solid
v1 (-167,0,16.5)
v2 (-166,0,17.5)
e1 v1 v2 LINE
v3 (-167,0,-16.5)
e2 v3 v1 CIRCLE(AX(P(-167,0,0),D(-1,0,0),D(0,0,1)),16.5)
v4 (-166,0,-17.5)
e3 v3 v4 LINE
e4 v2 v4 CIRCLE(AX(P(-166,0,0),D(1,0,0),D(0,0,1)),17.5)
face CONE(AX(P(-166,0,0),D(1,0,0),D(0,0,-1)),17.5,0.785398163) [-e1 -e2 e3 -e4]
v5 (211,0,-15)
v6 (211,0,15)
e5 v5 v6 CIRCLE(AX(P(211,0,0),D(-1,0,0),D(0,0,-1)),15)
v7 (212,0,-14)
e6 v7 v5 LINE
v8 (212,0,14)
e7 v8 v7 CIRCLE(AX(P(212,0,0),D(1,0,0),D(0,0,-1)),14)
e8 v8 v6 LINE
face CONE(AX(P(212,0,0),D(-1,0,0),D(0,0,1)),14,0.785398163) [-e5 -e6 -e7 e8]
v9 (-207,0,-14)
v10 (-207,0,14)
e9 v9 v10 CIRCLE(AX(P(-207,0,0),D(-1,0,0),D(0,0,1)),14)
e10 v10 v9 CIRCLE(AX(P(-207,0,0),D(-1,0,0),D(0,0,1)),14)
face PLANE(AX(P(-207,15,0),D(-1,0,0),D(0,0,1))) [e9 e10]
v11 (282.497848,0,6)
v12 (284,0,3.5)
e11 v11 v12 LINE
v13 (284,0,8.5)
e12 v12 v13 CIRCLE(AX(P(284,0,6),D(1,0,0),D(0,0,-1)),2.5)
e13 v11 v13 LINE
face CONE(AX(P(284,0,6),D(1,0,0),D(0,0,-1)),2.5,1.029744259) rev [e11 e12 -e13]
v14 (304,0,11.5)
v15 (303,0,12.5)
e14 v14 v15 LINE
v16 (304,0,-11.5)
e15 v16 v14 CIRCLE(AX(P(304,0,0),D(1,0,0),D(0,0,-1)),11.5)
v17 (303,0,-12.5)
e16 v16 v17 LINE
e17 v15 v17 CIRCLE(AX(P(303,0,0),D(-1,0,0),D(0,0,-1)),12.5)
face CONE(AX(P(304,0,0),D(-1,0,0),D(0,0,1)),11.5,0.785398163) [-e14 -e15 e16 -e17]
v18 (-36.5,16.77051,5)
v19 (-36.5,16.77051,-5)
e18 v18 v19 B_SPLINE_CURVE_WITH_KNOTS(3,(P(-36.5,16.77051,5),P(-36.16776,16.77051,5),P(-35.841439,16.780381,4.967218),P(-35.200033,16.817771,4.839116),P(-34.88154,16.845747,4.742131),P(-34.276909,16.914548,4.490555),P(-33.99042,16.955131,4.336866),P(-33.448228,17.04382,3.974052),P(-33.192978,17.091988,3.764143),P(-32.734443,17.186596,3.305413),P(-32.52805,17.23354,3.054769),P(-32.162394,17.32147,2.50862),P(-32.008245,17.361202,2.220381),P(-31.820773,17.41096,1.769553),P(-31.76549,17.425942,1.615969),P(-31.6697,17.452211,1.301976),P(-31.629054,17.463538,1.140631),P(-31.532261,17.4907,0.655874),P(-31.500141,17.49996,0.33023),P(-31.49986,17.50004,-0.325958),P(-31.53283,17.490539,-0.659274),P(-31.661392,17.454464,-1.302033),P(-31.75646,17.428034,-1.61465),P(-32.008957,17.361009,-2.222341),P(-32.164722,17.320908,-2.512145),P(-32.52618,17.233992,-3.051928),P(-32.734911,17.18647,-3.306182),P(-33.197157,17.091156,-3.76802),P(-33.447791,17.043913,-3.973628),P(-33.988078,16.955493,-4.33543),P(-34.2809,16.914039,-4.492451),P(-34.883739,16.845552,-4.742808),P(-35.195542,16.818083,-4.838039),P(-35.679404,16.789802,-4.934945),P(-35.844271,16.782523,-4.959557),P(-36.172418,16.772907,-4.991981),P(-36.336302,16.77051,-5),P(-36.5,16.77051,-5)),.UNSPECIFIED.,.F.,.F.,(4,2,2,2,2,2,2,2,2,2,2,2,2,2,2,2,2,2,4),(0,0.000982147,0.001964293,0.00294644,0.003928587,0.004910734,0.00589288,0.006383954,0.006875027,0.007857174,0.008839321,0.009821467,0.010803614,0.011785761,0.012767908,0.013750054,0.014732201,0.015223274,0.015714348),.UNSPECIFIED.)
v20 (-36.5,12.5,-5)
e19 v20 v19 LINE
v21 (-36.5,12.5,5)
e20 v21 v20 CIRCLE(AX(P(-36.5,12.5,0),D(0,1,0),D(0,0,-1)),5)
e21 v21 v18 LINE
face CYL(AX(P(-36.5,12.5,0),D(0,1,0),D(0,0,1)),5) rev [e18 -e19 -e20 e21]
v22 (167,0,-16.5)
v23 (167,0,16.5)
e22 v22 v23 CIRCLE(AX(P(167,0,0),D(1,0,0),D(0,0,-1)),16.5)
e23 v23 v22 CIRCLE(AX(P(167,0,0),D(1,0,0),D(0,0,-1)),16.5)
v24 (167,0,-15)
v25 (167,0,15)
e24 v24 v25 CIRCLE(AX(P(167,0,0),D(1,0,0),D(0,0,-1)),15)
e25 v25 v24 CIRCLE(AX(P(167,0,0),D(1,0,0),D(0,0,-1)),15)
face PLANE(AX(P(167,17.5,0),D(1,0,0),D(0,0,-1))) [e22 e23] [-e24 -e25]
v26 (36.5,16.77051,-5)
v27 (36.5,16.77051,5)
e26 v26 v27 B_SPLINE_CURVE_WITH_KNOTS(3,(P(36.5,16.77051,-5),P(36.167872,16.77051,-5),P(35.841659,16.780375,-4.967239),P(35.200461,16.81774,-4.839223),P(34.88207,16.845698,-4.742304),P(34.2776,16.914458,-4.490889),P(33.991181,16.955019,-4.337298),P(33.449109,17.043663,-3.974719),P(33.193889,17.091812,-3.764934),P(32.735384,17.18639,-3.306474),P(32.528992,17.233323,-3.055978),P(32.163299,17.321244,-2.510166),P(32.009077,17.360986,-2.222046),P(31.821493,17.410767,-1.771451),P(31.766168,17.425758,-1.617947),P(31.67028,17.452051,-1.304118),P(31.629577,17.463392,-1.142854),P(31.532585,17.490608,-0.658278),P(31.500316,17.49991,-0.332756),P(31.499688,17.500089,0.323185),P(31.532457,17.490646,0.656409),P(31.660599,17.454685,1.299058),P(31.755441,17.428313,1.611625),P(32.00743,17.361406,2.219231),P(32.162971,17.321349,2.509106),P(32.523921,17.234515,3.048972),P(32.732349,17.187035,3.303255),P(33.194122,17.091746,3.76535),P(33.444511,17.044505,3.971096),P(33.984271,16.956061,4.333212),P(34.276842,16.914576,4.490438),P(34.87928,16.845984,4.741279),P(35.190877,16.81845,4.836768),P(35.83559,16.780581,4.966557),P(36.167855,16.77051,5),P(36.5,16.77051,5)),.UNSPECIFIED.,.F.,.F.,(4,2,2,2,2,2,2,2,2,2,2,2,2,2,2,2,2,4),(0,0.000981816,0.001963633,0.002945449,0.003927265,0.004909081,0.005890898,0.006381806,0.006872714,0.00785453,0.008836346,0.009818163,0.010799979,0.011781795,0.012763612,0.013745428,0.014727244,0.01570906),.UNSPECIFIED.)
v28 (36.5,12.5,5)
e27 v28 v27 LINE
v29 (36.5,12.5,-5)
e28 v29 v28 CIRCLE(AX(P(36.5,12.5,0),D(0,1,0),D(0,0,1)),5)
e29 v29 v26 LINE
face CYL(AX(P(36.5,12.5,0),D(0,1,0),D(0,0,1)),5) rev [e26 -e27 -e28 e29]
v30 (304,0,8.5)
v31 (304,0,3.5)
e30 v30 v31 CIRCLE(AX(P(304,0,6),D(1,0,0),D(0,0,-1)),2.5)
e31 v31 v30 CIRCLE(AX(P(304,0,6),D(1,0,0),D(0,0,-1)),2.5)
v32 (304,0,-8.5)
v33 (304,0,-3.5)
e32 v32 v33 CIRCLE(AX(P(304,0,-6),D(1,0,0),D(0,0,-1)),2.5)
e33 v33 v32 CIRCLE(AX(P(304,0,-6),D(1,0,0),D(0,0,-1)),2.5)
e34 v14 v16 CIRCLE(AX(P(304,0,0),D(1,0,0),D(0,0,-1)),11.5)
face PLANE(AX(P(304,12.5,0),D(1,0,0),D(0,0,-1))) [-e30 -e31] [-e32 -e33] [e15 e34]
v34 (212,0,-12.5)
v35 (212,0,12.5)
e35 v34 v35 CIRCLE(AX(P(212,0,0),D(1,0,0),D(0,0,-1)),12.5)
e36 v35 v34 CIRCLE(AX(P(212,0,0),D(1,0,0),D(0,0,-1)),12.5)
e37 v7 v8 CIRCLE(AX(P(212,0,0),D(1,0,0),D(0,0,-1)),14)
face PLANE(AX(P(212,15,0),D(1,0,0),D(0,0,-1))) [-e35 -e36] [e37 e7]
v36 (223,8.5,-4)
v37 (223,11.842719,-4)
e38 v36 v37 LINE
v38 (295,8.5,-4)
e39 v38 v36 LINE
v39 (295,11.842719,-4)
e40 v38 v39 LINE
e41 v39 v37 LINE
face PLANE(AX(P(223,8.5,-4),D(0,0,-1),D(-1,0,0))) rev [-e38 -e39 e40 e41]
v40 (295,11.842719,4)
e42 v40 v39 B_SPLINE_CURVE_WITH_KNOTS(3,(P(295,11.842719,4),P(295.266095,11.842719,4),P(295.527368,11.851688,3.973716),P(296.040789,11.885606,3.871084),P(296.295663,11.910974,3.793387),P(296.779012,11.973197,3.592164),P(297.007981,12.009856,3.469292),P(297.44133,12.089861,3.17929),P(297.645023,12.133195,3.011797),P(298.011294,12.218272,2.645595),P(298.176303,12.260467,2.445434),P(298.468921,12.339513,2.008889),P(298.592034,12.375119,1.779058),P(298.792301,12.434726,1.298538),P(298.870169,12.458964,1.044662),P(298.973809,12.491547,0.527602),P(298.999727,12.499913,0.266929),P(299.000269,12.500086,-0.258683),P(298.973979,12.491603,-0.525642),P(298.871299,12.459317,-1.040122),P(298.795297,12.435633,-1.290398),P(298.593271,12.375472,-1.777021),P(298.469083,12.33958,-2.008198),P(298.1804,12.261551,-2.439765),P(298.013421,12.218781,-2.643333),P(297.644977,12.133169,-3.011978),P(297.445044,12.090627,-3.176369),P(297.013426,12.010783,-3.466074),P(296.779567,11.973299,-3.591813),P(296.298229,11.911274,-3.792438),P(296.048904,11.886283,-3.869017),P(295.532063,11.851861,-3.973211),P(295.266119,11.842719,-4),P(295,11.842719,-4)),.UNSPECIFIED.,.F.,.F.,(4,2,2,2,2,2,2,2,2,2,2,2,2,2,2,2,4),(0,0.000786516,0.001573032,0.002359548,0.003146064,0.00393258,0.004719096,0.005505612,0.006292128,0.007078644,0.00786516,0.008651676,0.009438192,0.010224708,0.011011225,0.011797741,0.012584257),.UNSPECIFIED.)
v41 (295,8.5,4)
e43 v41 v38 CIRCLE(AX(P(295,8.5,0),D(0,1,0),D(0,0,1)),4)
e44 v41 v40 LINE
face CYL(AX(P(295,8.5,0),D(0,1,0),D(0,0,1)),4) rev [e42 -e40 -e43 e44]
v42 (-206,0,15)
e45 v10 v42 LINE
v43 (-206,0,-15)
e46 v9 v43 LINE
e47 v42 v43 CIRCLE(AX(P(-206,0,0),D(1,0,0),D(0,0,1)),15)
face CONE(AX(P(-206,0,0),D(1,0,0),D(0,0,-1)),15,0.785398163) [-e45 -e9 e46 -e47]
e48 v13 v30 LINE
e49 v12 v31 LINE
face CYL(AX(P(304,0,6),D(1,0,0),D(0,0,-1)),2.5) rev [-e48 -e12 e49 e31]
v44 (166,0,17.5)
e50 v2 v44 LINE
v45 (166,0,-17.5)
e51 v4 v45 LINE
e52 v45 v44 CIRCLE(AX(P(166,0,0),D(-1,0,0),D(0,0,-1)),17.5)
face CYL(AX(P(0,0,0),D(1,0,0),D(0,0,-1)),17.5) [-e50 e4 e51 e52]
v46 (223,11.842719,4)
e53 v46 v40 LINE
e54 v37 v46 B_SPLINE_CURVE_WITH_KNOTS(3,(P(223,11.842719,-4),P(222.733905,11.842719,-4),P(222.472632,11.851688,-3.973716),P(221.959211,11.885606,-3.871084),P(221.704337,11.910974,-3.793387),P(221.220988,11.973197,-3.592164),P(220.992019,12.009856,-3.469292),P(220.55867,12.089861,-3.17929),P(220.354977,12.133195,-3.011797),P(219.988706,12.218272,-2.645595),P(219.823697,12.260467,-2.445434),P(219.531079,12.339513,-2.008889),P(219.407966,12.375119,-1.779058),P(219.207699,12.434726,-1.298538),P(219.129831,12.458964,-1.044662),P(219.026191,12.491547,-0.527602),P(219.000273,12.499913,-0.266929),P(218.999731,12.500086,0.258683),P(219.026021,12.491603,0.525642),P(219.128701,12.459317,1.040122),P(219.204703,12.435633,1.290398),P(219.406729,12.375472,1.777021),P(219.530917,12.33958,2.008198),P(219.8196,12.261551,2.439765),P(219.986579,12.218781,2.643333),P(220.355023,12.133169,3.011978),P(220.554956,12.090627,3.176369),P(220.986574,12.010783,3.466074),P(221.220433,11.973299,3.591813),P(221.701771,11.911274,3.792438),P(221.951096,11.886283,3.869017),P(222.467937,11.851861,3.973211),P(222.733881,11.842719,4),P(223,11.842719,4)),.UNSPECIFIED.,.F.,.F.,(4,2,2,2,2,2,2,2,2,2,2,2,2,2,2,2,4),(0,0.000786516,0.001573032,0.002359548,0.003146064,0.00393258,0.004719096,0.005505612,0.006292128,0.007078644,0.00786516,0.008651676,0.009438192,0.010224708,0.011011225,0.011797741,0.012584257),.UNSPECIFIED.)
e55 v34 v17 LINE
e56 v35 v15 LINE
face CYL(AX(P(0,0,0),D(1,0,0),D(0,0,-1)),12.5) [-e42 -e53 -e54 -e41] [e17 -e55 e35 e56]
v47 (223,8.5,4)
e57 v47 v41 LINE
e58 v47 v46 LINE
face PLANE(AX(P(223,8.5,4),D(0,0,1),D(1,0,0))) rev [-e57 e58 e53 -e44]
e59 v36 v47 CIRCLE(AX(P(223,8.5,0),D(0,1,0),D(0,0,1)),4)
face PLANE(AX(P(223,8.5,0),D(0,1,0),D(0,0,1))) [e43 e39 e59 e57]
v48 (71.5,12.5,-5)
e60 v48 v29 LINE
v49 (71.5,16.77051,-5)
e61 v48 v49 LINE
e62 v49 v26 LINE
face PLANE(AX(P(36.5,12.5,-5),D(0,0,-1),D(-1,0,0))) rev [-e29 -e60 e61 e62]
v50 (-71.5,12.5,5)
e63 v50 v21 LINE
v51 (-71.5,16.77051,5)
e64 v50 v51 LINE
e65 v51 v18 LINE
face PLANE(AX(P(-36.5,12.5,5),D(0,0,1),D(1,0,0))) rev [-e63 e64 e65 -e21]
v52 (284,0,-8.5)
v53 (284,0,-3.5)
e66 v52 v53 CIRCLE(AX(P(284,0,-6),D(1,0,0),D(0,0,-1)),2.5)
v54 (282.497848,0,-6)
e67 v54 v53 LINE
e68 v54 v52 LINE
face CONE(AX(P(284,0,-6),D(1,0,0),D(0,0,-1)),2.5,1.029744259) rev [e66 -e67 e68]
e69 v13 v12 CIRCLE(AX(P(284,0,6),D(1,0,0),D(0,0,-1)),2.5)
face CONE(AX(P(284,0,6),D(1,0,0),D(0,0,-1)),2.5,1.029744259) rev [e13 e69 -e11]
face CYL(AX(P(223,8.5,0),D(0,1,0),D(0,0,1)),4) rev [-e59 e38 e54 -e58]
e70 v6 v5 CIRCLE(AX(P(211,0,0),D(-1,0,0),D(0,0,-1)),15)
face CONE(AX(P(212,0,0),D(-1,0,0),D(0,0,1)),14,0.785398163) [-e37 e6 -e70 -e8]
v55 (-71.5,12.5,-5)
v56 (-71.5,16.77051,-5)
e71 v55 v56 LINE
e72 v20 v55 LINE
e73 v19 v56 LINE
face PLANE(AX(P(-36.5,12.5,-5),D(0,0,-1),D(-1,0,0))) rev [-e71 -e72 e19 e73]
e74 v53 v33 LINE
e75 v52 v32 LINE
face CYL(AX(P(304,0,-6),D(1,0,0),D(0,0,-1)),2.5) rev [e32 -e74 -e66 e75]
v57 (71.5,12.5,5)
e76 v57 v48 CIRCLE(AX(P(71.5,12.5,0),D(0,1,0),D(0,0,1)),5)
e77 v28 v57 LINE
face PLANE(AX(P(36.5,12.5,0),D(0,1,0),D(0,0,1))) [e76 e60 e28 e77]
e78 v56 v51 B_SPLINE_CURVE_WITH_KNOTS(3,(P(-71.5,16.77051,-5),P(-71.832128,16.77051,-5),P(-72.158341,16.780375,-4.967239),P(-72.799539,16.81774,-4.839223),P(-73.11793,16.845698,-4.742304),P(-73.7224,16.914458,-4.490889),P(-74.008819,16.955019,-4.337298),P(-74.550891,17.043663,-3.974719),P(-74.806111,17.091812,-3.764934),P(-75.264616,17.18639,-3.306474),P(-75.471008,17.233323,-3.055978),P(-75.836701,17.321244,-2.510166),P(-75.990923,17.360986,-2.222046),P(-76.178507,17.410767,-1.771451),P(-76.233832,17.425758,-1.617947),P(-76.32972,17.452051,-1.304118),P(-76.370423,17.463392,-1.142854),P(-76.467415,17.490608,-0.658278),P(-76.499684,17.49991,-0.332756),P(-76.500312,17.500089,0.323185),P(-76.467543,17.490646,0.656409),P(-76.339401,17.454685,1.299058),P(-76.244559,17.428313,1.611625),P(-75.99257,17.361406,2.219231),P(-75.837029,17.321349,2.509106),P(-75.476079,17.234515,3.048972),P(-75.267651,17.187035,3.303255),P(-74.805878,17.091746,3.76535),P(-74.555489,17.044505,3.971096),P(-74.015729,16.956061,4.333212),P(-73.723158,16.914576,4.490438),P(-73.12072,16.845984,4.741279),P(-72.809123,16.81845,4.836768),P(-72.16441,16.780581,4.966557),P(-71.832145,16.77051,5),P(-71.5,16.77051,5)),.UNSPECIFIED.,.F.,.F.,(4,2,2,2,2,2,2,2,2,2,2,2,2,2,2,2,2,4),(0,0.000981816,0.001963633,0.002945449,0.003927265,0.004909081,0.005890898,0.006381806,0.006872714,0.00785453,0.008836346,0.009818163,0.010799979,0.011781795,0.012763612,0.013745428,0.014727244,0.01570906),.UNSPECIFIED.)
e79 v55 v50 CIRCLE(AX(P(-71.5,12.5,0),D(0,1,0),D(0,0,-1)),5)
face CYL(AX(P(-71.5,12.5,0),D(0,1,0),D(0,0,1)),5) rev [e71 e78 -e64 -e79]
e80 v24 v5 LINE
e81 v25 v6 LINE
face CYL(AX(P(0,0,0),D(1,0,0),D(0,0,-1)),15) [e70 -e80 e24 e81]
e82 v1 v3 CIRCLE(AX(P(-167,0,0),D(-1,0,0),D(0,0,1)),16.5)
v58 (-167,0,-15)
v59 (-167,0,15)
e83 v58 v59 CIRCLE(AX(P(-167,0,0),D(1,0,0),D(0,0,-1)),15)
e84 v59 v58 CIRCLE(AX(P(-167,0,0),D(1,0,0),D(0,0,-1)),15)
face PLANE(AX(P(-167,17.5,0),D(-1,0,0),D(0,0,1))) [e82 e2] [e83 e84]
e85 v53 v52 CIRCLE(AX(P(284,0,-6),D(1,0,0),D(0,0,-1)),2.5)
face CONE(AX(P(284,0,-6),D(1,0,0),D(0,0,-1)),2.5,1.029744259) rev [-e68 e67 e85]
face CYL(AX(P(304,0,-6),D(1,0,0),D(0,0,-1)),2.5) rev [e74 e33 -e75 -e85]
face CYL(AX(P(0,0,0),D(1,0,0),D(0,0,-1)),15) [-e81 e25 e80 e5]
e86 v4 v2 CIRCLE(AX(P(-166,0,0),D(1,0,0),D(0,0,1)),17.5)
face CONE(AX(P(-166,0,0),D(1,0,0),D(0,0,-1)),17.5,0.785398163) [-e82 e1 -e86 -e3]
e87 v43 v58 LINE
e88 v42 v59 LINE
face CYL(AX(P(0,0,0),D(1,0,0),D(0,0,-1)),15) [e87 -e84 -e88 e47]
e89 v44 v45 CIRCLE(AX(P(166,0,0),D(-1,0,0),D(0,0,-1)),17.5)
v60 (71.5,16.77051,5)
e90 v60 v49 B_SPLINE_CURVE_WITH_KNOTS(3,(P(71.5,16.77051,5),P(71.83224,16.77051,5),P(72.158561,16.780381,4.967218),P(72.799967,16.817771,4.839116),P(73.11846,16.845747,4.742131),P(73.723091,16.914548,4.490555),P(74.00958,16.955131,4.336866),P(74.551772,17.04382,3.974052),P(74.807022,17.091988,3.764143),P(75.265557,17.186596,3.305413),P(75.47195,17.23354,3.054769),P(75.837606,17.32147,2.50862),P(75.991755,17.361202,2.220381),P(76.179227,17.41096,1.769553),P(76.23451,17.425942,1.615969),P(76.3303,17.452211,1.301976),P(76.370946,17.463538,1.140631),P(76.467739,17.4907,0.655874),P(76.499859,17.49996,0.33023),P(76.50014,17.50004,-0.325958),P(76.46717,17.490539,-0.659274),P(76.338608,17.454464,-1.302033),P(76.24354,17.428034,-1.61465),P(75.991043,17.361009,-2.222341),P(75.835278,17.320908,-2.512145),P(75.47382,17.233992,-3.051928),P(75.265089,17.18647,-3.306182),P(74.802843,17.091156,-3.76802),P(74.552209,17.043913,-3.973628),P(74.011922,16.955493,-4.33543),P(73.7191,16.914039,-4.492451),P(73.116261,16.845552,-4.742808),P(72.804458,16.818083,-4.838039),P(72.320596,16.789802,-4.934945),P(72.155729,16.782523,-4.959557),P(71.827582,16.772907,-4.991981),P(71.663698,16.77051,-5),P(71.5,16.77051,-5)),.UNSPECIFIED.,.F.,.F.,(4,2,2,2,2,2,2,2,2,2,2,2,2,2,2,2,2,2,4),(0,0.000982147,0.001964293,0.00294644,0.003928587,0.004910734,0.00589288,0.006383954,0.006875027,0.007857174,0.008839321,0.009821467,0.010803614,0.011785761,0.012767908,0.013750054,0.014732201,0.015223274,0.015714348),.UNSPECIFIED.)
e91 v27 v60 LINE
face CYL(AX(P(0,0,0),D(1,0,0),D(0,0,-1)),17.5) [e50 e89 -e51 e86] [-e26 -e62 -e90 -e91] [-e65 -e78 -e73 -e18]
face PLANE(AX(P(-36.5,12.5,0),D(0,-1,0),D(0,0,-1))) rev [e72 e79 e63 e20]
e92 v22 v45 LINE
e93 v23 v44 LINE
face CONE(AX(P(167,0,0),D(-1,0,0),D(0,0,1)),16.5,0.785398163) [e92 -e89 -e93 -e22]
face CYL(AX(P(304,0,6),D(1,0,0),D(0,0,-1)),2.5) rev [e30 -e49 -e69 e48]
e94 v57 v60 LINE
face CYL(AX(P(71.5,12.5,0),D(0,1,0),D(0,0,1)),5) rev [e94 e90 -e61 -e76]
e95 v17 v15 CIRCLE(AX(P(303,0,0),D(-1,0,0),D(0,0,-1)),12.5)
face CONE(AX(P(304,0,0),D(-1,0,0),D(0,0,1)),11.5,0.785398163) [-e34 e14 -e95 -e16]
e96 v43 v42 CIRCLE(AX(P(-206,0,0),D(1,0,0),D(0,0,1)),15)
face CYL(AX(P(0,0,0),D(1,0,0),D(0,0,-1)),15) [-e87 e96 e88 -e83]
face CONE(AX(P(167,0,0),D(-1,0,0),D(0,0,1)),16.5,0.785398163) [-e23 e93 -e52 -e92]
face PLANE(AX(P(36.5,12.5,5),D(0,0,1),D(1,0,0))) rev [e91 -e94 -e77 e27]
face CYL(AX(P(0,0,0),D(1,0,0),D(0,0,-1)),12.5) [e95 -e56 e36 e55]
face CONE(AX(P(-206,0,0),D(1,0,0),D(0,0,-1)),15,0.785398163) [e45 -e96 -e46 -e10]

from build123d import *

# Parameters (mm, degrees)
CUT_EXTRUDE_1_DEPTH    = 5
CUT_EXTRUDE_2_DEPTH    = 4
CHAMFER_1_SIZE         = 1
HOLE_WIZARD_M6_1_D     = 5
HOLE_WIZARD_M6_1_DEPTH = 20
HOLE_WIZARD_M6_1_TIP   = 1.502151548


with BuildPart() as part:
    # 草图1 → 旋转1 (revolve)
    with BuildSketch(Plane.XY, mode=Mode.PRIVATE) as revolve_1_sk:
        Polygon((167, 17.5), (0, 17.5), (-167, 17.5), (-167, 15), (-207, 15), (-207, 0), (304, 0), (304, 12.5), (212, 12.5), (212, 15), (167, 15), align=None)
    revolve(revolve_1_sk.sketch.rotate(Axis((0, 0, 0), (-1, 0, 0)), 90), axis=Axis((0, 0, 0), (-1, 0, 0)))

    # 草图2 → 切除-拉伸1 (cut)
    with BuildSketch(Plane(origin=(0, 17.5, 0), x_dir=(1, 0, 0), z_dir=(0, 1, 0))):
        with BuildLine():
            Line((36.5, 5), (71.5, 5))
            ThreePointArc((71.5, 5), (76.5, 0), (71.5, -5))
            Line((71.5, -5), (36.5, -5))
            ThreePointArc((36.5, -5), (31.5, 0), (36.5, 5))
        make_face()
        with BuildLine():
            Line((-36.5, 5), (-71.5, 5))
            ThreePointArc((-71.5, 5), (-76.5, 0), (-71.5, -5))
            Line((-71.5, -5), (-36.5, -5))
            ThreePointArc((-36.5, -5), (-31.5, 0), (-36.5, 5))
        make_face()
    extrude(amount=-CUT_EXTRUDE_1_DEPTH, mode=Mode.SUBTRACT)

    # 草图3 → 切除-拉伸2 (cut)
    with BuildSketch(Plane(origin=(0, 12.5, 0), x_dir=(1, 0, 0), z_dir=(0, 1, 0))):
        with BuildLine():
            Line((223, 4), (295, 4))
            ThreePointArc((295, 4), (299, 0), (295, -4))
            Line((295, -4), (223, -4))
            ThreePointArc((223, -4), (219, 0), (223, 4))
        make_face()
    extrude(amount=-CUT_EXTRUDE_2_DEPTH, mode=Mode.SUBTRACT)

    # 倒角1
    chamfer_1_edges = [part.edges().sort_by_distance(p)[0] for p in [
        (-207, 0, 15),
        (-167, 0, 17.5),
        (167, 0, 17.5),
        (212, 0, 15),
        (304, 0, 12.5),
    ]]
    chamfer(chamfer_1_edges, length=CHAMFER_1_SIZE)

    # M6 螺纹孔1
    with Locations(Plane(origin=(304, 0, 0), x_dir=(0, 0, -1), z_dir=(1, 0, 0))):
        with Locations((6, 0), (-6, 0)):
            Hole(HOLE_WIZARD_M6_1_D / 2, depth=HOLE_WIZARD_M6_1_DEPTH)
            with Locations((0, 0, -(HOLE_WIZARD_M6_1_DEPTH + HOLE_WIZARD_M6_1_TIP / 2))):  # 118° drill point
                Cone(0, HOLE_WIZARD_M6_1_D / 2, HOLE_WIZARD_M6_1_TIP, mode=Mode.SUBTRACT)


solid = part.part
